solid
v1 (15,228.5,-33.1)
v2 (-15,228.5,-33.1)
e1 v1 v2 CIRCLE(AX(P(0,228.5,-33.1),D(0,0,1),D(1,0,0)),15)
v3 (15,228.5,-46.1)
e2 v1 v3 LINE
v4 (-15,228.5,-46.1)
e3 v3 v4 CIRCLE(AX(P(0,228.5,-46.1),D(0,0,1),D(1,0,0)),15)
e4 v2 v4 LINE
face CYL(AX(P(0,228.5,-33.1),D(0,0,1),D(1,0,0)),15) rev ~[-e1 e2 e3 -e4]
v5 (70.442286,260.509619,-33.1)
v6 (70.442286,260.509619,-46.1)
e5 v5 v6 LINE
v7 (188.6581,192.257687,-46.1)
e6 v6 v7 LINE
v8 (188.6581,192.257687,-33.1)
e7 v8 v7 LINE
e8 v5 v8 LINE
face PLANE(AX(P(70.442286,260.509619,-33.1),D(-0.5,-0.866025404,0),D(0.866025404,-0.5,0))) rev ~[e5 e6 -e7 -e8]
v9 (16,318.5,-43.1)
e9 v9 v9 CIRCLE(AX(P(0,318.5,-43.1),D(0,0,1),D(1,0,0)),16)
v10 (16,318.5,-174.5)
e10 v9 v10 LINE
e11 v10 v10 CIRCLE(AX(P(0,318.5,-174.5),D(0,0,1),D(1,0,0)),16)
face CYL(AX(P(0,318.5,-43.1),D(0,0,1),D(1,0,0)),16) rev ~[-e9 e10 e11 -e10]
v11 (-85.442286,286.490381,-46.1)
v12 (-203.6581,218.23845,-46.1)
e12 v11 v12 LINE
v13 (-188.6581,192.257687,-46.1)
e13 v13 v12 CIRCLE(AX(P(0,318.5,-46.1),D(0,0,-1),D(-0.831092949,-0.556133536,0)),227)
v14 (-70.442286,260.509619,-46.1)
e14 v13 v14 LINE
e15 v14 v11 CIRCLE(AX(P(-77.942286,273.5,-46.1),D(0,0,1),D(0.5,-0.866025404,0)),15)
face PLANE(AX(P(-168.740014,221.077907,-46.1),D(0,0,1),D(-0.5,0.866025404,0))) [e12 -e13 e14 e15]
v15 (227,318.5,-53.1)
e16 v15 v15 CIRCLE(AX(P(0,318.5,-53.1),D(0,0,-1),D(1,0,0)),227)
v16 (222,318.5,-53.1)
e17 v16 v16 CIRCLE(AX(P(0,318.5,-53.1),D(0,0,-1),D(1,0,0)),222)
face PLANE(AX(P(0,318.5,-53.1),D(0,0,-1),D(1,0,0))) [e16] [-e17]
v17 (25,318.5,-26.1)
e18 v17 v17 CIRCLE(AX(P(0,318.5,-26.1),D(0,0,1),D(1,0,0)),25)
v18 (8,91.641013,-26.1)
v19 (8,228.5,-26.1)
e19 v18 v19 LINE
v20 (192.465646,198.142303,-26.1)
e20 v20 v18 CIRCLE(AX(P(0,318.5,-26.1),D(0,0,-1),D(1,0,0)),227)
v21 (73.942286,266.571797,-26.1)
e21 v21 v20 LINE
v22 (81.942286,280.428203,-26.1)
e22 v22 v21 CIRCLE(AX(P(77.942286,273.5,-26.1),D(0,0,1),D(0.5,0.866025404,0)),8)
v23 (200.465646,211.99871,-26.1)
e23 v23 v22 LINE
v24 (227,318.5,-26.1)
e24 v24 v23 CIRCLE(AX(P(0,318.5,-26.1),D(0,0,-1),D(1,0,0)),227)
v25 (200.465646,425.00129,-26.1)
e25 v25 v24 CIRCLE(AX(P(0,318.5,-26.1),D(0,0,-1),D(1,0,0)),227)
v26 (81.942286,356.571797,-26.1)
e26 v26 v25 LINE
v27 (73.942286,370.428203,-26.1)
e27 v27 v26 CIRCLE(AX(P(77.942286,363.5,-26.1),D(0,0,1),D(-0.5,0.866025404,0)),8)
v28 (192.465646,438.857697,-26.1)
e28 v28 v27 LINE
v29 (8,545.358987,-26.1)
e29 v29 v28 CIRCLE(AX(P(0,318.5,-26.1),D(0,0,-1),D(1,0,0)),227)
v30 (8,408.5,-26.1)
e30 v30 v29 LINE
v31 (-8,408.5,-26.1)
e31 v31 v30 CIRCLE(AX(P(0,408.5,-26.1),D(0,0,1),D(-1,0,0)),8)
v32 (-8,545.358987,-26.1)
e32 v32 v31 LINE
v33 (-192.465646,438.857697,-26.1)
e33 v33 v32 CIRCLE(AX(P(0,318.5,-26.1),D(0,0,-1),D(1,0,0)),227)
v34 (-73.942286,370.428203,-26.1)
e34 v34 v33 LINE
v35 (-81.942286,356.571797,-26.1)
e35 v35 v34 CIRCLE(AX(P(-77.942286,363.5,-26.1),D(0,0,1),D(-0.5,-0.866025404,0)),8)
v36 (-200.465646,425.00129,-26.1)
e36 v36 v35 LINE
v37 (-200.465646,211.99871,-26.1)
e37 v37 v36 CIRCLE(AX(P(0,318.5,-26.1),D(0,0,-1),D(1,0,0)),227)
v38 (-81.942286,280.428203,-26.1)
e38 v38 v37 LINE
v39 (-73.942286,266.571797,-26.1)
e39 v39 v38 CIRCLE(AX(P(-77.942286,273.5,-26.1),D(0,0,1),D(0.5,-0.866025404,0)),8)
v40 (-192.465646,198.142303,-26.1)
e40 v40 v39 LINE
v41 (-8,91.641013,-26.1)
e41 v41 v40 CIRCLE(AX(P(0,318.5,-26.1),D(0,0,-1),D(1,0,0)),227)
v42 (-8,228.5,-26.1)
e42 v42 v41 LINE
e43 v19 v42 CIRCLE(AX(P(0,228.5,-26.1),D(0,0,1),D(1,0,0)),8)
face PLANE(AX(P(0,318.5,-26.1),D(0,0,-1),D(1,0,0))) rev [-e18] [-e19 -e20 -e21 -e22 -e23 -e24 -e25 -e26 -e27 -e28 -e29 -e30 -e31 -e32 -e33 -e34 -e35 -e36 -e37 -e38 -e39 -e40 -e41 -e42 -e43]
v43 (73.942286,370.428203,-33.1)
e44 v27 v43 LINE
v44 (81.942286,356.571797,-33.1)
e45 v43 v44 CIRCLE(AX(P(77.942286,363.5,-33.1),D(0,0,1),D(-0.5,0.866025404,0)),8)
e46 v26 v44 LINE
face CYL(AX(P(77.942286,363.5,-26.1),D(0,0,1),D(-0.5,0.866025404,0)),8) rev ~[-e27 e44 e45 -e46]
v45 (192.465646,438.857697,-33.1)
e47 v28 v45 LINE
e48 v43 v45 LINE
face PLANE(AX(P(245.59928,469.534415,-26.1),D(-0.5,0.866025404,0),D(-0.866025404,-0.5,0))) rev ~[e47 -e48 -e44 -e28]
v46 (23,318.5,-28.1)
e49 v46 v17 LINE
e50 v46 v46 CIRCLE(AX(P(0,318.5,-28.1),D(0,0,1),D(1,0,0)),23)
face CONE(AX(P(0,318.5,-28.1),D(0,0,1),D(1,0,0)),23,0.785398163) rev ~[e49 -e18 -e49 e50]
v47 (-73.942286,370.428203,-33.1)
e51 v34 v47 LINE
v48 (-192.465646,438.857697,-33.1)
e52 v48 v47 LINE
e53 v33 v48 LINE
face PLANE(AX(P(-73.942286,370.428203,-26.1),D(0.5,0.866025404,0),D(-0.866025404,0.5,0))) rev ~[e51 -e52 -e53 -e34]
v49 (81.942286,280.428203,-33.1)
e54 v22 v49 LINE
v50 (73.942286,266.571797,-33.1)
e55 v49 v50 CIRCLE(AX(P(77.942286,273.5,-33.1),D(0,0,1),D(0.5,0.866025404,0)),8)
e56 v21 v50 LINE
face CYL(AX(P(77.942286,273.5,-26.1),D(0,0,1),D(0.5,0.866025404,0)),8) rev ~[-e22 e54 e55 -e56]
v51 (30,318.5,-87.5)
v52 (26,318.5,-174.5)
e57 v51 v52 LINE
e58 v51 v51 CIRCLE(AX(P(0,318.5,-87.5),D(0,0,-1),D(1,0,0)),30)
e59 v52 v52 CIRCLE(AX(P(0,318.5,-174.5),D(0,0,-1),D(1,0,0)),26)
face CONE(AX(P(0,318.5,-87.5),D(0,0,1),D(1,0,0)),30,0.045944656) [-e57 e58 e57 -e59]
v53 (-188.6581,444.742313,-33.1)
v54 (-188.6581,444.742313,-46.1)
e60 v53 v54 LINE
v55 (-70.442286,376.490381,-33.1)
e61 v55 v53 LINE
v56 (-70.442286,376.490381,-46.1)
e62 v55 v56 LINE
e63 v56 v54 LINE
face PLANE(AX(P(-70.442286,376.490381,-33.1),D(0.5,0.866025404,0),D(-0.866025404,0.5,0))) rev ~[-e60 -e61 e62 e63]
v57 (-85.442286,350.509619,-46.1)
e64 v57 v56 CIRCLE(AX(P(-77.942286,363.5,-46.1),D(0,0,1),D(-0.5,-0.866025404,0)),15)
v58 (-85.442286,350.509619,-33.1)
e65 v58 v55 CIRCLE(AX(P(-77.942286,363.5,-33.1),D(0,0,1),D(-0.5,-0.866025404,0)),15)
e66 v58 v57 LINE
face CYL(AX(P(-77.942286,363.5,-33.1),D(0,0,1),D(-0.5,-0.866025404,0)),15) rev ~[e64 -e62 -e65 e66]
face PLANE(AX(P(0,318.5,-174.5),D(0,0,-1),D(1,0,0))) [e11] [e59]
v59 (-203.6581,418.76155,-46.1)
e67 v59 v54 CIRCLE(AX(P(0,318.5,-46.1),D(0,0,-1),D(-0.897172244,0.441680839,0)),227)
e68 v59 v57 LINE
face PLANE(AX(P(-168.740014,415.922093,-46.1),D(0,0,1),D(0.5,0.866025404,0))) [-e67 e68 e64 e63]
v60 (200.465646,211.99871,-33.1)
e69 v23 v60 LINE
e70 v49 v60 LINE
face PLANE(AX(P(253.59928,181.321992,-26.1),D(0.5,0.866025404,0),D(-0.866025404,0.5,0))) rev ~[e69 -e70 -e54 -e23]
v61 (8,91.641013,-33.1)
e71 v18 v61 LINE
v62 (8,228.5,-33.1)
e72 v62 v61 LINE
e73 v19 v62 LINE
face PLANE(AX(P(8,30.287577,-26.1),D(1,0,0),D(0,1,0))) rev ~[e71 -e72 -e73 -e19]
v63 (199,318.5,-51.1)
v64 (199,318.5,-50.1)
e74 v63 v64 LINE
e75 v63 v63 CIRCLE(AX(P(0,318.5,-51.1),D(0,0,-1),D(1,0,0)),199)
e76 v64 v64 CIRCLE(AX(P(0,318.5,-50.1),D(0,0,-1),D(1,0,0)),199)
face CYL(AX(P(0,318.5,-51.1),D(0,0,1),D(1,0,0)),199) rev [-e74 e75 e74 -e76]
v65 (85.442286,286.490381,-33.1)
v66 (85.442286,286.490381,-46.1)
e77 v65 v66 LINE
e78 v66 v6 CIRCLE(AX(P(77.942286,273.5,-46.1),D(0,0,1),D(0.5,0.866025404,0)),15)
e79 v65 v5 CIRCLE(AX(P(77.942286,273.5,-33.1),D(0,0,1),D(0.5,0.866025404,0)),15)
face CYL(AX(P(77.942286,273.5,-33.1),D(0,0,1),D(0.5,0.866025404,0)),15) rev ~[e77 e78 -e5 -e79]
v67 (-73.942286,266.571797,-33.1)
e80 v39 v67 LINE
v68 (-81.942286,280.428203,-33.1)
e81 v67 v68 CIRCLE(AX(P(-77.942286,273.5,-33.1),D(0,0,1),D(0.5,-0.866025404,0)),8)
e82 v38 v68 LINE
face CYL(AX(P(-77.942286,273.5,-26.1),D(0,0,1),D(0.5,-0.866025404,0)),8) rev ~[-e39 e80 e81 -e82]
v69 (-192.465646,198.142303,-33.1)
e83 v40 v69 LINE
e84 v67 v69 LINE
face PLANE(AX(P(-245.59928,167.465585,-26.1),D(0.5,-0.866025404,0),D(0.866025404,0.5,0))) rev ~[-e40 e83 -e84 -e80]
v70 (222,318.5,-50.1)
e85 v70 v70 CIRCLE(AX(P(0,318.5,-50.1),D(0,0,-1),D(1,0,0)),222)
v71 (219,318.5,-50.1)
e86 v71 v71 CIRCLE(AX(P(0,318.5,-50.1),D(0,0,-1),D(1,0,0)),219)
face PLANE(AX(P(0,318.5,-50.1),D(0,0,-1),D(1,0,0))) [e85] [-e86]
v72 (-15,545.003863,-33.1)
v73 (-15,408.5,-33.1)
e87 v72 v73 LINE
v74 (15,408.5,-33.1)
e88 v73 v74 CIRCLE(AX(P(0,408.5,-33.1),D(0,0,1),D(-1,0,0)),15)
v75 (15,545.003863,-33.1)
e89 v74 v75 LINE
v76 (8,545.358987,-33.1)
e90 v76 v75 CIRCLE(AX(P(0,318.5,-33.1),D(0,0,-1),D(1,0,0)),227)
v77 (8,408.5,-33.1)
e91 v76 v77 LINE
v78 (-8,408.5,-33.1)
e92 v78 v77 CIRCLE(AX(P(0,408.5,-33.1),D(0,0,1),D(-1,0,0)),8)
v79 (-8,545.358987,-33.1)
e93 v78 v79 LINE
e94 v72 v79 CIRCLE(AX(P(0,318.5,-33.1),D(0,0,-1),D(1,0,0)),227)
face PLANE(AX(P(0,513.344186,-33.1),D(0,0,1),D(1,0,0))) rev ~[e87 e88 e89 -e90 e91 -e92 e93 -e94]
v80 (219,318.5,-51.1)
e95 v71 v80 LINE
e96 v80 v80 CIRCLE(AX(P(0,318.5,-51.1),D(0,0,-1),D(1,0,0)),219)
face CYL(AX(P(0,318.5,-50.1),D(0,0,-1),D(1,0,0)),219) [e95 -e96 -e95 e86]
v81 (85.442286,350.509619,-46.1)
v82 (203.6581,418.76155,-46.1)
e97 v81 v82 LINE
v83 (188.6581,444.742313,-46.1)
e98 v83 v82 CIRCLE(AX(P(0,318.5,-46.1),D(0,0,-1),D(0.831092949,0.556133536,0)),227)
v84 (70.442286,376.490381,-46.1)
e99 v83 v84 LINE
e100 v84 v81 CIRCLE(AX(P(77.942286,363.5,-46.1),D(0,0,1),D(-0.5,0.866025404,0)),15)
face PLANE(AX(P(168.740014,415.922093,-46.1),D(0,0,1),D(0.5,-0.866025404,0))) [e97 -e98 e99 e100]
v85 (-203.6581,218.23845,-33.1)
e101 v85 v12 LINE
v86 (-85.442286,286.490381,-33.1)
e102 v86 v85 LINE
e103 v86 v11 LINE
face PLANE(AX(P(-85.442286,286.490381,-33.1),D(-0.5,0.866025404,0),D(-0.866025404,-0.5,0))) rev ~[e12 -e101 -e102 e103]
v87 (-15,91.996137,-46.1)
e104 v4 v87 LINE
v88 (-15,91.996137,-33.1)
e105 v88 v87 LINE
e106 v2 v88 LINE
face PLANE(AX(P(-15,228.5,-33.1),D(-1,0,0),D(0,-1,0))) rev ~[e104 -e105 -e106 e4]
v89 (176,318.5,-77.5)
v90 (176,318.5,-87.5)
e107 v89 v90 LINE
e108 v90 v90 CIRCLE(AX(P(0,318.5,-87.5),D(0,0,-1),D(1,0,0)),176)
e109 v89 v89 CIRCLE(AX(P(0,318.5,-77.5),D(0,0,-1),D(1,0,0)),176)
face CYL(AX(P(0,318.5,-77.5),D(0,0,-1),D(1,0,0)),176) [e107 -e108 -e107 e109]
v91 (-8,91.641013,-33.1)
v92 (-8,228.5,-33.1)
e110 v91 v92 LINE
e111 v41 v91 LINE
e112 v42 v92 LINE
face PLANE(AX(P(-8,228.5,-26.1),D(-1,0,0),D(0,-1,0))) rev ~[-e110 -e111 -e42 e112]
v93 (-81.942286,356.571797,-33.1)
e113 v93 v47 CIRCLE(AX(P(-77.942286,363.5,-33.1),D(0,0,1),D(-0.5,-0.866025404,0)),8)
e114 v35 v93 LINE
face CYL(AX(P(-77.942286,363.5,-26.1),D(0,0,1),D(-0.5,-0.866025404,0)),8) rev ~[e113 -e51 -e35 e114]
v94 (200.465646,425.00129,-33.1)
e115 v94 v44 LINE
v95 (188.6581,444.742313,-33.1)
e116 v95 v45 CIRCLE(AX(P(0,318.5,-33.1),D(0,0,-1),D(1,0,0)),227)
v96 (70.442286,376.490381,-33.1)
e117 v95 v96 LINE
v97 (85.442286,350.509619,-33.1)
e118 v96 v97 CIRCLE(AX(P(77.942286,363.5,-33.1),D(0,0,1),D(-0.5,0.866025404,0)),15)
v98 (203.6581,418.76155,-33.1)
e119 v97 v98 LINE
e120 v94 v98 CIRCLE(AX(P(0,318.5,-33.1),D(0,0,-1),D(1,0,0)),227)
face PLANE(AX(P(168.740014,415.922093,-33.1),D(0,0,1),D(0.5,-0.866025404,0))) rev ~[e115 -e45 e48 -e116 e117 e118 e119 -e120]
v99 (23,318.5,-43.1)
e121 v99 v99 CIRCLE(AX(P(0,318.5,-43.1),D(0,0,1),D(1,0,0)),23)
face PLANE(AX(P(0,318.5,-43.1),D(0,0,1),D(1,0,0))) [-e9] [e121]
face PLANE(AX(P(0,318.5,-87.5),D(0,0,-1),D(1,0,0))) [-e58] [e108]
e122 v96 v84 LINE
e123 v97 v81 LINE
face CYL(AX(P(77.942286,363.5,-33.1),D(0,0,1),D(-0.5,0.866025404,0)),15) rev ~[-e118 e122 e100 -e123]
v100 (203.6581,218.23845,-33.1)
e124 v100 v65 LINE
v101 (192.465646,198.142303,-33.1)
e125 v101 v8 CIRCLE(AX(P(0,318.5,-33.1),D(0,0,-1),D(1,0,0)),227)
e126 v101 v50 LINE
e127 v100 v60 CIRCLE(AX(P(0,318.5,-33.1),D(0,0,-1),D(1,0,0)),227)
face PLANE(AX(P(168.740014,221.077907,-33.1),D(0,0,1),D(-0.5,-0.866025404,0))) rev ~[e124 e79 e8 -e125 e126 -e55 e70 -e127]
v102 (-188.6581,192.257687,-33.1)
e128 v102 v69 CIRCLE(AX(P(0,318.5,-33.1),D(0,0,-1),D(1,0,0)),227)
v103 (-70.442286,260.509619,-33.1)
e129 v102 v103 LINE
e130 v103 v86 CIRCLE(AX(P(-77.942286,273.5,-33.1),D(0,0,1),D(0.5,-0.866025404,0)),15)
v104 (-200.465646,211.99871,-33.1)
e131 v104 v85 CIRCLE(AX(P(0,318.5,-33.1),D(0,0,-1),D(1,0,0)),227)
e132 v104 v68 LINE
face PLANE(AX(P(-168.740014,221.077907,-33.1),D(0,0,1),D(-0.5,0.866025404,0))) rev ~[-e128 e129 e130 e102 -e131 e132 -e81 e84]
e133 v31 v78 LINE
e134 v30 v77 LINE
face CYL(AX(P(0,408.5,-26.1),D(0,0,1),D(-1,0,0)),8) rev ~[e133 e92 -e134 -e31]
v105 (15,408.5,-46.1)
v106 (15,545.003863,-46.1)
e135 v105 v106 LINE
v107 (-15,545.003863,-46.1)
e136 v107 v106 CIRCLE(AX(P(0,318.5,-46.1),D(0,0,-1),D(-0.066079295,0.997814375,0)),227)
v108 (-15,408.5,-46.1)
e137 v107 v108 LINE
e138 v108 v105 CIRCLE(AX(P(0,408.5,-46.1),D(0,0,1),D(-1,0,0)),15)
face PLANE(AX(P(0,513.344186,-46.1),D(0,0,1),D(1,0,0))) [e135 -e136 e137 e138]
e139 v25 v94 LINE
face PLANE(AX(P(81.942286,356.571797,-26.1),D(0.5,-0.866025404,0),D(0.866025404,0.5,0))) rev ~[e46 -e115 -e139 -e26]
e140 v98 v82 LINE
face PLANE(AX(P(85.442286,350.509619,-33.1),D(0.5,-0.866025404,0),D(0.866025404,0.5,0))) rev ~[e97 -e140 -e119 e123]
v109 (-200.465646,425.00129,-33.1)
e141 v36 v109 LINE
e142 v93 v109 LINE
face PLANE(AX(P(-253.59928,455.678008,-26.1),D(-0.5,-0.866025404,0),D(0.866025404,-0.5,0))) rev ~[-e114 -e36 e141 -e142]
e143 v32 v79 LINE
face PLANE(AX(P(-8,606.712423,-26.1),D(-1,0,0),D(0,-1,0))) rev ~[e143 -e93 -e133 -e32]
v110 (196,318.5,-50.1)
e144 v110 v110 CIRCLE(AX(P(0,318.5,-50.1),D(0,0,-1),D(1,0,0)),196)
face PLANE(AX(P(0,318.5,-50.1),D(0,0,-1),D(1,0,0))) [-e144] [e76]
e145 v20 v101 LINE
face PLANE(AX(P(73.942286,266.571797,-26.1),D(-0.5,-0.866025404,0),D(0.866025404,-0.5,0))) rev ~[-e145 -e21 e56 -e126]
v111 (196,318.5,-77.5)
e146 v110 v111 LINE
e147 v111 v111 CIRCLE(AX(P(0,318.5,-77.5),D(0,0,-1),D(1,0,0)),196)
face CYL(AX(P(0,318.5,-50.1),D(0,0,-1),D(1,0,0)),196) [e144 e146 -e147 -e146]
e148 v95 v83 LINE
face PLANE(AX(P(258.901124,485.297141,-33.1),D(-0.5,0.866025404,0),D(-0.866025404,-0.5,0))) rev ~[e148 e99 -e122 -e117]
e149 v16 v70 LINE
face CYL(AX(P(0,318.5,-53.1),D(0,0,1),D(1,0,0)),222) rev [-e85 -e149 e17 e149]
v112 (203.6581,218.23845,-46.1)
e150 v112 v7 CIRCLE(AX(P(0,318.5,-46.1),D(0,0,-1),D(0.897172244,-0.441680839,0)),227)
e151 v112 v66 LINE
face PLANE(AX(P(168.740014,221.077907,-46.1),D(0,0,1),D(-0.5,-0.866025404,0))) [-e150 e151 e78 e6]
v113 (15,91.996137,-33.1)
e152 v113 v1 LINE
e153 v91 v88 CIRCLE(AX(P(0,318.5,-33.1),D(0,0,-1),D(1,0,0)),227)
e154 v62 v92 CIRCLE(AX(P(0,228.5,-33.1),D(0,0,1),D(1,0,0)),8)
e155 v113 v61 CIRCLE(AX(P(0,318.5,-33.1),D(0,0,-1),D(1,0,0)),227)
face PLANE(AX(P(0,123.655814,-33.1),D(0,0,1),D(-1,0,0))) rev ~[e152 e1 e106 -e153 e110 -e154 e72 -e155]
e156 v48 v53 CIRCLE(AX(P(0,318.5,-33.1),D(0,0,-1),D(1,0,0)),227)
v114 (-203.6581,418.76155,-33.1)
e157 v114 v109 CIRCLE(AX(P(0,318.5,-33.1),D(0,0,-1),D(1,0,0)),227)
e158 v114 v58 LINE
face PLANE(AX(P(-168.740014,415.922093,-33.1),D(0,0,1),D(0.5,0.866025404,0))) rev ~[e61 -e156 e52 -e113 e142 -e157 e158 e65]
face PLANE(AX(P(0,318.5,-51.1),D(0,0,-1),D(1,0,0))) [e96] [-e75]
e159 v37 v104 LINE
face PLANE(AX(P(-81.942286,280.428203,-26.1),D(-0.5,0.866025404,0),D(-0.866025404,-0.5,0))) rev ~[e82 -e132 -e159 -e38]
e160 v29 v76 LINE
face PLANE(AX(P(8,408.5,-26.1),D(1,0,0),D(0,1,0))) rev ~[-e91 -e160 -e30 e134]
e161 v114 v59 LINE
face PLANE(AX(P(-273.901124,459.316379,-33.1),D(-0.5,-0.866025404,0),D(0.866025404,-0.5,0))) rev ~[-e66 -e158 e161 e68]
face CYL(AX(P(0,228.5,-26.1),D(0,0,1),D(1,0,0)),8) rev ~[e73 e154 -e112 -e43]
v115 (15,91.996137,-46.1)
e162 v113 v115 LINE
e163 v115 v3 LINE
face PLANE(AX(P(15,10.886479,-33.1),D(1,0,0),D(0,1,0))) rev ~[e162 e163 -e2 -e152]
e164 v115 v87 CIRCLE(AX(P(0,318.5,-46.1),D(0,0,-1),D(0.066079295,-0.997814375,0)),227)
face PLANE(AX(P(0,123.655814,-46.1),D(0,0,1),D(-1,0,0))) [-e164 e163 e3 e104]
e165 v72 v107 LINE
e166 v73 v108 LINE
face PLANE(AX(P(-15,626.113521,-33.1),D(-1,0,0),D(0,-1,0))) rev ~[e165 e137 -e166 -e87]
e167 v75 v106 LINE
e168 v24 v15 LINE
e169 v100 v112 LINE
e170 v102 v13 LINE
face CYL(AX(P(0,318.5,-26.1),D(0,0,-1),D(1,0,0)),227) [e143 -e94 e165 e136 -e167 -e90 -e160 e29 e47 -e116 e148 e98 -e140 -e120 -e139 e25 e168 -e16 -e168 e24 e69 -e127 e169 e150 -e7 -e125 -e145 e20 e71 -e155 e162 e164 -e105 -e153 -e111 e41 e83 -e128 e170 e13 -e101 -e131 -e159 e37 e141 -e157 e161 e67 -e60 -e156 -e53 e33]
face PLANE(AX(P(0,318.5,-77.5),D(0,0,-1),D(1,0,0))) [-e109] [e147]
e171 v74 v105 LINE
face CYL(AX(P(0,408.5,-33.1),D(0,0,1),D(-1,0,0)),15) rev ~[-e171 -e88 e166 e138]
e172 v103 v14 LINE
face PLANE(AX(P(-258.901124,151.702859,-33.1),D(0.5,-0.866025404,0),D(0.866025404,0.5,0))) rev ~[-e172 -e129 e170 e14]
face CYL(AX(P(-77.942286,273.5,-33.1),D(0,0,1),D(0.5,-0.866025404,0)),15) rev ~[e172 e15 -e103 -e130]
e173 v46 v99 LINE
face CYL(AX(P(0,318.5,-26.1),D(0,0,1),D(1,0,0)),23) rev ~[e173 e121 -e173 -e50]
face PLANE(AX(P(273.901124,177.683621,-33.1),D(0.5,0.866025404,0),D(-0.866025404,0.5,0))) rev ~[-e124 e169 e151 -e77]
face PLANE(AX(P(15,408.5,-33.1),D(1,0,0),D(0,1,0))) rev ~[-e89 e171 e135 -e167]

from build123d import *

# Parameters (mm, degrees)
SKETCH2_R          = 23
CUT_EXTRUDE1_DEPTH = 17
SKETCH3_R          = 16
CUT_EXTRUDE2_DEPTH = 606.281099986
CHAMFER1_SIZE      = 2
CUT_EXTRUDE3_DEPTH = 20
CUT_EXTRUDE4_DEPTH = 13
CIRPATTERN1_COUNT  = 6


with BuildPart() as part:
    # Sketch1 → Revolve1 (revolve)
    with BuildSketch(Plane(origin=(0, 318.5, 0), x_dir=(-1, 0, 0), z_dir=(0, -1, 0)), mode=Mode.PRIVATE) as revolve1_sk:
        Polygon((176, 77.5), (176, 87.5), (30, 87.5), (26, 174.5), (0, 174.5), (0, 26.1), (227, 26.1), (227, 53.1), (222, 53.1), (222, 50.1), (219, 50.1), (219, 51.1), (199, 51.1), (199, 50.1), (196, 50.1), (196, 51.1), (196, 77.5), align=None)
    revolve(revolve1_sk.sketch.rotate(Axis((0, 318.5, 0), (0, 0, -1)), 180), axis=Axis((0, 318.5, 0), (0, 0, -1)))

    # Sketch2 → Cut-Extrude1 (cut)
    with BuildSketch(Plane.XY.offset(-26.1)):
        with Locations((0, 318.5)):
            Circle(SKETCH2_R)
    extrude(amount=-CUT_EXTRUDE1_DEPTH, mode=Mode.SUBTRACT)

    # Sketch3 → Cut-Extrude2 (cut, through all)
    with BuildSketch(Plane.XY.offset(-43.1)):
        with Locations((0, 318.5)):
            Circle(SKETCH3_R)
    extrude(amount=-CUT_EXTRUDE2_DEPTH, mode=Mode.SUBTRACT)

    # Chamfer1
    chamfer1_edges = [part.edges().sort_by_distance(p)[0] for p in [
        (-23, 318.5, -26.1),
    ]]
    chamfer(chamfer1_edges, length=CHAMFER1_SIZE)

    # Sketch4 → Cut-Extrude3 (cut)
    with BuildSketch(Plane.XY.offset(-26.1)):
        with BuildLine():
            Line((-8, 606.712422614), (-8, 408.5))
            ThreePointArc((-8, 408.5), (0, 400.5), (8, 408.5))
            Line((8, 408.5), (8, 606.712422614))
            Line((8, 606.712422614), (-8, 606.712422614))
        make_face()
    cut_extrude3 = extrude(amount=-CUT_EXTRUDE3_DEPTH, mode=Mode.SUBTRACT)

    # Sketch5 → Cut-Extrude4 (cut)
    with BuildSketch(Plane.XY.offset(-33.1)):
        with BuildLine():
            Line((-15, 626.113520772), (-15, 408.5))
            ThreePointArc((-15, 408.5), (0, 393.5), (15, 408.5))
            Line((15, 408.5), (15, 626.113520772))
            Line((15, 626.113520772), (-15, 626.113520772))
        make_face()
    cut_extrude4 = extrude(amount=-CUT_EXTRUDE4_DEPTH, mode=Mode.SUBTRACT)

    # CirPattern1: Cut-Extrude3, Cut-Extrude4 ×6 about axis
    cirpattern1_axis = Axis((0, 318.5, 0), (0, 0, 1))
    add([cut_extrude3.rotate(cirpattern1_axis, i * 360 / CIRPATTERN1_COUNT) for i in range(1, CIRPATTERN1_COUNT)], mode=Mode.SUBTRACT)
    add([cut_extrude4.rotate(cirpattern1_axis, i * 360 / CIRPATTERN1_COUNT) for i in range(1, CIRPATTERN1_COUNT)], mode=Mode.SUBTRACT)


solid = part.part
